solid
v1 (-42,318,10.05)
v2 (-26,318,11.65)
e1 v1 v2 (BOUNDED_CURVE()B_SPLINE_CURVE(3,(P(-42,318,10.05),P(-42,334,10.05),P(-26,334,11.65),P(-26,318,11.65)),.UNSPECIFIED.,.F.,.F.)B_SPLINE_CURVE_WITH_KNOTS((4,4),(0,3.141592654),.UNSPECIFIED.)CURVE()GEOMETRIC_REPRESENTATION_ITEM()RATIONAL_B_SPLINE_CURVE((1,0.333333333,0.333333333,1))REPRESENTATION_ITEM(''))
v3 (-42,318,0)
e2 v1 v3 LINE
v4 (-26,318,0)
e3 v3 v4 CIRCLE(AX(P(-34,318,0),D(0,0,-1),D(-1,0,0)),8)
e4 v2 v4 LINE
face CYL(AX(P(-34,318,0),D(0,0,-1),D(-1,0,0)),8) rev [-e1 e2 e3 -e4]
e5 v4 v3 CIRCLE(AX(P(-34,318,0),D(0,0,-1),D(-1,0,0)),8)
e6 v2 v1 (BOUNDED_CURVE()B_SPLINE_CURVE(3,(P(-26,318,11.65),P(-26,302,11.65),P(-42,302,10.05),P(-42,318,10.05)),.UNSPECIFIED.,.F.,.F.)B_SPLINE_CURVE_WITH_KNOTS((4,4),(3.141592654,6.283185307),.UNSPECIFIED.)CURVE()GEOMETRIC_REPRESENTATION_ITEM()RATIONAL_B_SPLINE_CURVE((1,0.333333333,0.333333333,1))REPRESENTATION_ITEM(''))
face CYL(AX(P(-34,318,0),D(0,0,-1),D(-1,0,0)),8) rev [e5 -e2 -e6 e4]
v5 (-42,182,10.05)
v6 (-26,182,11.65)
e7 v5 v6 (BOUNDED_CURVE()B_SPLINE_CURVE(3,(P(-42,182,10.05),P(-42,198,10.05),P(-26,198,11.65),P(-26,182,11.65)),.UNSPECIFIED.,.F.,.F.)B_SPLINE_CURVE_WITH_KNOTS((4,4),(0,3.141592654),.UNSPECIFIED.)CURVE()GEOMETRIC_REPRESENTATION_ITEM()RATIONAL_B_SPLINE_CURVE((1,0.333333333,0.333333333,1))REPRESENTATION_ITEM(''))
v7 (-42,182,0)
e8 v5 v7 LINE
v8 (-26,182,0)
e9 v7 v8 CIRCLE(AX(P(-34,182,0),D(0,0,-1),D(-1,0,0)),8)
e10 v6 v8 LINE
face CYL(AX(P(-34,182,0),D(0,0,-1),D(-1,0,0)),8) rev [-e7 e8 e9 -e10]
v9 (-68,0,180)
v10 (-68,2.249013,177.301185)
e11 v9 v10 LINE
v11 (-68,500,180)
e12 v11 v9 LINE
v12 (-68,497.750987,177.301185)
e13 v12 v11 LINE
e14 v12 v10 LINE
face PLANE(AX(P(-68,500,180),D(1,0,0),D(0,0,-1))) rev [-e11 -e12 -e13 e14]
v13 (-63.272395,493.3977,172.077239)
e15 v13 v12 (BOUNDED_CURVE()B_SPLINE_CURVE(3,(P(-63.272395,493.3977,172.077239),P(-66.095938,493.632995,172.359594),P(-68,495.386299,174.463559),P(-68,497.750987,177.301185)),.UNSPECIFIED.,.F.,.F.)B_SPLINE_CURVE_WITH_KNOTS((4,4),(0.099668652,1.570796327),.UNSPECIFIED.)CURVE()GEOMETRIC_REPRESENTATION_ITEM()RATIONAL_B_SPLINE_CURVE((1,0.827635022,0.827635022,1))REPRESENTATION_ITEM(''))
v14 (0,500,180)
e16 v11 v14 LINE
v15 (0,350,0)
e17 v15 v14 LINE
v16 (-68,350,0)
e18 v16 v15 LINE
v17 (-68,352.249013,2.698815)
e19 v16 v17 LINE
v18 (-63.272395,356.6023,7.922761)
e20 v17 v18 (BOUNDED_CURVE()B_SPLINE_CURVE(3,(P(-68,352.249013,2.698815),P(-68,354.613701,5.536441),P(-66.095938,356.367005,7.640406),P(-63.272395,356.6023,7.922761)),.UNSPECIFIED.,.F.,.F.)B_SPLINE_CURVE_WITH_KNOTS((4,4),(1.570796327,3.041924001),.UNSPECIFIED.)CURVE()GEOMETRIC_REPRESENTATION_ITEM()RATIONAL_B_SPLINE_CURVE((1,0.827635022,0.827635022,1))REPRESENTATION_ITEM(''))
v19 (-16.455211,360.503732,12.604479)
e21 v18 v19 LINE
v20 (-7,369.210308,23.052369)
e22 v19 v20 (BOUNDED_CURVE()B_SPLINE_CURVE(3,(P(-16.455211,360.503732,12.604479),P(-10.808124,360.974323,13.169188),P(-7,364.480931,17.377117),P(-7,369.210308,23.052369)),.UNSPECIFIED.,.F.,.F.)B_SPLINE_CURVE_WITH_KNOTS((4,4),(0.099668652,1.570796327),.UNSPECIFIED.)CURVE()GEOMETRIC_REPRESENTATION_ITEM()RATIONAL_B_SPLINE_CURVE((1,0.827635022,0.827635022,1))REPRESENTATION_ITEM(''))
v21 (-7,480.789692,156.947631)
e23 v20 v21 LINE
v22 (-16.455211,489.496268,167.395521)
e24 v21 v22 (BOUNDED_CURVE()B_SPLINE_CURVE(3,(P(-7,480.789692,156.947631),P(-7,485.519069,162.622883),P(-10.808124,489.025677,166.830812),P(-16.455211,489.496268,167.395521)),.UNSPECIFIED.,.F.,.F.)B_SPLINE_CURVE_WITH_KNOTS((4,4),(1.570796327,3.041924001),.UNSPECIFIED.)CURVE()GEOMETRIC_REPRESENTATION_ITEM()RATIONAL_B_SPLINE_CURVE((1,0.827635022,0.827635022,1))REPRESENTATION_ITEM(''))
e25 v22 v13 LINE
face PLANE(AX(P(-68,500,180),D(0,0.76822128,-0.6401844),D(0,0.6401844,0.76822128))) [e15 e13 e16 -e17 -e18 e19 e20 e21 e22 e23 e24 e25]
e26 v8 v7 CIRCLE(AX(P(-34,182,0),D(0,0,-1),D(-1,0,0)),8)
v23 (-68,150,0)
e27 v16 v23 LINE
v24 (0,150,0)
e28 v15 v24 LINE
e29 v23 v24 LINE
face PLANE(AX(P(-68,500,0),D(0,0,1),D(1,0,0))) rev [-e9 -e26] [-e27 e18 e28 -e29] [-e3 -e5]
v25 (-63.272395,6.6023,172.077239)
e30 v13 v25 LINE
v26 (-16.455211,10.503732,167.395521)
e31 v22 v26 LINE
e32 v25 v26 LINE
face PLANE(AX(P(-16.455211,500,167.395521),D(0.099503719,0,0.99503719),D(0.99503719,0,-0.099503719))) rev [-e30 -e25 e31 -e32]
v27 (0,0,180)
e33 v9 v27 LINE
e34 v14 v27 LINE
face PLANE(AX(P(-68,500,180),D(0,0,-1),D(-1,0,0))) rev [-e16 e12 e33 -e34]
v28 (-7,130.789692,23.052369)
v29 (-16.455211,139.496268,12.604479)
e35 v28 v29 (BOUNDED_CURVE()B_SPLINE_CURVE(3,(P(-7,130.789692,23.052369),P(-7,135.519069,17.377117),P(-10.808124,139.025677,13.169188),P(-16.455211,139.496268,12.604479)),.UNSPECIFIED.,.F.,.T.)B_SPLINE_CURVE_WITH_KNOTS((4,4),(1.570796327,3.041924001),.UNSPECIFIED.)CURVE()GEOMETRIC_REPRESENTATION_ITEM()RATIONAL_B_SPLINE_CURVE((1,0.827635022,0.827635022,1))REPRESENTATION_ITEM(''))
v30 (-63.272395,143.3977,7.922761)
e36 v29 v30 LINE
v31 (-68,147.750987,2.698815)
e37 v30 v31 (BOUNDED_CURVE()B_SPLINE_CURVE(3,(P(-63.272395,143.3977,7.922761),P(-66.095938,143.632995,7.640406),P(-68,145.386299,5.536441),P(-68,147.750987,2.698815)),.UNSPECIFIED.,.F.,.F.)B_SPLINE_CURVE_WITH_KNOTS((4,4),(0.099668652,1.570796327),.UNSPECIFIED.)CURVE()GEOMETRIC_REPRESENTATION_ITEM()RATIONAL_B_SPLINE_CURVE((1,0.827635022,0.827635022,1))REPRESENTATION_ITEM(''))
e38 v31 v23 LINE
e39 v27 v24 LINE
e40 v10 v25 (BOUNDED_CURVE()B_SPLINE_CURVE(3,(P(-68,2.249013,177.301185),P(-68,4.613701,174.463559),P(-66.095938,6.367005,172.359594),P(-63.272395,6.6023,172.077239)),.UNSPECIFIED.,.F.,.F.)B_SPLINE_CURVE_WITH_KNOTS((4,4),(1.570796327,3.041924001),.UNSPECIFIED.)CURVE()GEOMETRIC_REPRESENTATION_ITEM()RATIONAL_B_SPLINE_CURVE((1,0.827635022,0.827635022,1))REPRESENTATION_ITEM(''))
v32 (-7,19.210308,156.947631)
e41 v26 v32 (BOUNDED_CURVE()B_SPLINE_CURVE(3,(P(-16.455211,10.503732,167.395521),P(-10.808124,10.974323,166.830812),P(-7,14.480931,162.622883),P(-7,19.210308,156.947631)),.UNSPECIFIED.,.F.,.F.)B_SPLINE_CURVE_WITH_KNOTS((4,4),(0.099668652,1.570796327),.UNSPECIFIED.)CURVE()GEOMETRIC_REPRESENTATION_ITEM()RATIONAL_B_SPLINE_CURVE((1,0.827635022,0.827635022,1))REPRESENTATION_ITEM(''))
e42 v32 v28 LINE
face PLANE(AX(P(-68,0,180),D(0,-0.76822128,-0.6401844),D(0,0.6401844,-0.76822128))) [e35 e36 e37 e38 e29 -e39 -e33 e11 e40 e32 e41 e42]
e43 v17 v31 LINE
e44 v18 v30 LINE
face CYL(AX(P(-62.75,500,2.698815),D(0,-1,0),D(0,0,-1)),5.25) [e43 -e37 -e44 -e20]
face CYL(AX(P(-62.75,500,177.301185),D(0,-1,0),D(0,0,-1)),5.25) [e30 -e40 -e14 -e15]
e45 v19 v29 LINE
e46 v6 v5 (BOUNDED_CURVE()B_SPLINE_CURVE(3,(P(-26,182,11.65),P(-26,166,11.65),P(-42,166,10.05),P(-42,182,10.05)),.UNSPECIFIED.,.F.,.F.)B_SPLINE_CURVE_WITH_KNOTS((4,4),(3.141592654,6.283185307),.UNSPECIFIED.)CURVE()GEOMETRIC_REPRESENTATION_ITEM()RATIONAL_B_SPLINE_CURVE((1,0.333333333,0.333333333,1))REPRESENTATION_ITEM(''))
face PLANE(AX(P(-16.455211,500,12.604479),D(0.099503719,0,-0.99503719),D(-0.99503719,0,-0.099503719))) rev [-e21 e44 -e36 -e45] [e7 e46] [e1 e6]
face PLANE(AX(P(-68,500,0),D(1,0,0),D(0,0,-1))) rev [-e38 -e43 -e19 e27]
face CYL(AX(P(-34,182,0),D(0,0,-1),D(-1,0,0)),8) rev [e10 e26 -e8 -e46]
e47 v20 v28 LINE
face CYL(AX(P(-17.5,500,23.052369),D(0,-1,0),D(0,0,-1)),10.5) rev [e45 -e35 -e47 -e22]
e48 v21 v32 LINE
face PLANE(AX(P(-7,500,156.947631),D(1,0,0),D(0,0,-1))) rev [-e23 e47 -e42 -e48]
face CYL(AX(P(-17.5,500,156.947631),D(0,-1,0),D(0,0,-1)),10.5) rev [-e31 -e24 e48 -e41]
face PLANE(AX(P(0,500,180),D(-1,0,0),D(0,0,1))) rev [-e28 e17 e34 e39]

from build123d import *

# Parameters (mm, degrees)
GB_T707_1988_18A_XXXXXXXXXXXXXXX528V9_2_DEPTH = 500
CUT_EXTRUDE_1_DEPTH                           = 536.746208573
HOLE_WIZARD_16_0_16_1_REACH                   = 537.746
HOLE_WIZARD_16_0_16_1_BORE_R                  = 8


with BuildPart() as part:
    # Sketch11 → 热轧普通槽钢(gb t707-1988) 18A-XXXXXXXXXXXXXXX528V9(2) (new body)
    with BuildSketch(Plane(origin=(0, 0, 0), x_dir=(-1, 0, 0), z_dir=(0, 1, 0))):
        with BuildLine():
            Line((68, 180), (0, 180))
            Line((0, 180), (0, 0))
            Line((0, 0), (68, 0))
            Line((68, 0), (68, 2.698815299))
            ThreePointArc((68, 2.698815299), (66.642625801, 6.221593233), (63.272394525, 7.922760548))
            Line((63.272394525, 7.922760548), (16.45521095, 12.604478905))
            ThreePointArc((16.45521095, 12.604478905), (9.714748398, 16.006813534), (7, 23.052369402))
            Line((7, 23.052369402), (7, 156.947630598))
            ThreePointArc((7, 156.947630598), (9.714748398, 163.993186466), (16.45521095, 167.395521095))
            Line((16.45521095, 167.395521095), (63.272394525, 172.077239452))
            ThreePointArc((63.272394525, 172.077239452), (66.642625801, 173.778406767), (68, 177.301184701))
            Line((68, 177.301184701), (68, 180))
        make_face()
    extrude(amount=GB_T707_1988_18A_XXXXXXXXXXXXXXX528V9_2_DEPTH)

    # 草图8 → 切除-拉伸1 (cut, through all)
    with BuildSketch(Plane(origin=(0, 0, 180), x_dir=(0, 0, 1), z_dir=(-1, 0, 0))):
        Polygon((0, 500), (-180, 350), (-180, 500), align=None)
        Polygon((-180, 0), (0, 0), (-180, 150), align=None)
    extrude(amount=CUT_EXTRUDE_1_DEPTH, mode=Mode.SUBTRACT)

    # Ø16.0 (16) 直径孔1 bore → Ø16.0 (16) 直径孔1 (cut, up to next)
    with BuildSketch(Plane(origin=(0, 0, 0), x_dir=(-1, 0, 0), z_dir=(0, 0, -1)), mode=Mode.PRIVATE) as hole_wizard_16_0_16_1_sk1:
        with Locations((34, 318)):
            Circle(HOLE_WIZARD_16_0_16_1_BORE_R)
    hole_wizard_16_0_16_1_tool1 = extrude(hole_wizard_16_0_16_1_sk1.sketch, amount=-HOLE_WIZARD_16_0_16_1_REACH, mode=Mode.PRIVATE) & part.part
    # Ø16.0 (16) 直径孔1 bore → Ø16.0 (16) 直径孔1 (cut, up to next)
    with BuildSketch(Plane(origin=(0, 0, 0), x_dir=(-1, 0, 0), z_dir=(0, 0, -1)), mode=Mode.PRIVATE) as hole_wizard_16_0_16_1_sk2:
        with Locations((34, 182)):
            Circle(HOLE_WIZARD_16_0_16_1_BORE_R)
    hole_wizard_16_0_16_1_tool2 = extrude(hole_wizard_16_0_16_1_sk2.sketch, amount=-HOLE_WIZARD_16_0_16_1_REACH, mode=Mode.PRIVATE) & part.part
    add(hole_wizard_16_0_16_1_tool1.solids().sort_by_distance((-34, 318, 0))[0], mode=Mode.SUBTRACT)
    add(hole_wizard_16_0_16_1_tool2.solids().sort_by_distance((-34, 182, 0))[0], mode=Mode.SUBTRACT)


solid = part.part
